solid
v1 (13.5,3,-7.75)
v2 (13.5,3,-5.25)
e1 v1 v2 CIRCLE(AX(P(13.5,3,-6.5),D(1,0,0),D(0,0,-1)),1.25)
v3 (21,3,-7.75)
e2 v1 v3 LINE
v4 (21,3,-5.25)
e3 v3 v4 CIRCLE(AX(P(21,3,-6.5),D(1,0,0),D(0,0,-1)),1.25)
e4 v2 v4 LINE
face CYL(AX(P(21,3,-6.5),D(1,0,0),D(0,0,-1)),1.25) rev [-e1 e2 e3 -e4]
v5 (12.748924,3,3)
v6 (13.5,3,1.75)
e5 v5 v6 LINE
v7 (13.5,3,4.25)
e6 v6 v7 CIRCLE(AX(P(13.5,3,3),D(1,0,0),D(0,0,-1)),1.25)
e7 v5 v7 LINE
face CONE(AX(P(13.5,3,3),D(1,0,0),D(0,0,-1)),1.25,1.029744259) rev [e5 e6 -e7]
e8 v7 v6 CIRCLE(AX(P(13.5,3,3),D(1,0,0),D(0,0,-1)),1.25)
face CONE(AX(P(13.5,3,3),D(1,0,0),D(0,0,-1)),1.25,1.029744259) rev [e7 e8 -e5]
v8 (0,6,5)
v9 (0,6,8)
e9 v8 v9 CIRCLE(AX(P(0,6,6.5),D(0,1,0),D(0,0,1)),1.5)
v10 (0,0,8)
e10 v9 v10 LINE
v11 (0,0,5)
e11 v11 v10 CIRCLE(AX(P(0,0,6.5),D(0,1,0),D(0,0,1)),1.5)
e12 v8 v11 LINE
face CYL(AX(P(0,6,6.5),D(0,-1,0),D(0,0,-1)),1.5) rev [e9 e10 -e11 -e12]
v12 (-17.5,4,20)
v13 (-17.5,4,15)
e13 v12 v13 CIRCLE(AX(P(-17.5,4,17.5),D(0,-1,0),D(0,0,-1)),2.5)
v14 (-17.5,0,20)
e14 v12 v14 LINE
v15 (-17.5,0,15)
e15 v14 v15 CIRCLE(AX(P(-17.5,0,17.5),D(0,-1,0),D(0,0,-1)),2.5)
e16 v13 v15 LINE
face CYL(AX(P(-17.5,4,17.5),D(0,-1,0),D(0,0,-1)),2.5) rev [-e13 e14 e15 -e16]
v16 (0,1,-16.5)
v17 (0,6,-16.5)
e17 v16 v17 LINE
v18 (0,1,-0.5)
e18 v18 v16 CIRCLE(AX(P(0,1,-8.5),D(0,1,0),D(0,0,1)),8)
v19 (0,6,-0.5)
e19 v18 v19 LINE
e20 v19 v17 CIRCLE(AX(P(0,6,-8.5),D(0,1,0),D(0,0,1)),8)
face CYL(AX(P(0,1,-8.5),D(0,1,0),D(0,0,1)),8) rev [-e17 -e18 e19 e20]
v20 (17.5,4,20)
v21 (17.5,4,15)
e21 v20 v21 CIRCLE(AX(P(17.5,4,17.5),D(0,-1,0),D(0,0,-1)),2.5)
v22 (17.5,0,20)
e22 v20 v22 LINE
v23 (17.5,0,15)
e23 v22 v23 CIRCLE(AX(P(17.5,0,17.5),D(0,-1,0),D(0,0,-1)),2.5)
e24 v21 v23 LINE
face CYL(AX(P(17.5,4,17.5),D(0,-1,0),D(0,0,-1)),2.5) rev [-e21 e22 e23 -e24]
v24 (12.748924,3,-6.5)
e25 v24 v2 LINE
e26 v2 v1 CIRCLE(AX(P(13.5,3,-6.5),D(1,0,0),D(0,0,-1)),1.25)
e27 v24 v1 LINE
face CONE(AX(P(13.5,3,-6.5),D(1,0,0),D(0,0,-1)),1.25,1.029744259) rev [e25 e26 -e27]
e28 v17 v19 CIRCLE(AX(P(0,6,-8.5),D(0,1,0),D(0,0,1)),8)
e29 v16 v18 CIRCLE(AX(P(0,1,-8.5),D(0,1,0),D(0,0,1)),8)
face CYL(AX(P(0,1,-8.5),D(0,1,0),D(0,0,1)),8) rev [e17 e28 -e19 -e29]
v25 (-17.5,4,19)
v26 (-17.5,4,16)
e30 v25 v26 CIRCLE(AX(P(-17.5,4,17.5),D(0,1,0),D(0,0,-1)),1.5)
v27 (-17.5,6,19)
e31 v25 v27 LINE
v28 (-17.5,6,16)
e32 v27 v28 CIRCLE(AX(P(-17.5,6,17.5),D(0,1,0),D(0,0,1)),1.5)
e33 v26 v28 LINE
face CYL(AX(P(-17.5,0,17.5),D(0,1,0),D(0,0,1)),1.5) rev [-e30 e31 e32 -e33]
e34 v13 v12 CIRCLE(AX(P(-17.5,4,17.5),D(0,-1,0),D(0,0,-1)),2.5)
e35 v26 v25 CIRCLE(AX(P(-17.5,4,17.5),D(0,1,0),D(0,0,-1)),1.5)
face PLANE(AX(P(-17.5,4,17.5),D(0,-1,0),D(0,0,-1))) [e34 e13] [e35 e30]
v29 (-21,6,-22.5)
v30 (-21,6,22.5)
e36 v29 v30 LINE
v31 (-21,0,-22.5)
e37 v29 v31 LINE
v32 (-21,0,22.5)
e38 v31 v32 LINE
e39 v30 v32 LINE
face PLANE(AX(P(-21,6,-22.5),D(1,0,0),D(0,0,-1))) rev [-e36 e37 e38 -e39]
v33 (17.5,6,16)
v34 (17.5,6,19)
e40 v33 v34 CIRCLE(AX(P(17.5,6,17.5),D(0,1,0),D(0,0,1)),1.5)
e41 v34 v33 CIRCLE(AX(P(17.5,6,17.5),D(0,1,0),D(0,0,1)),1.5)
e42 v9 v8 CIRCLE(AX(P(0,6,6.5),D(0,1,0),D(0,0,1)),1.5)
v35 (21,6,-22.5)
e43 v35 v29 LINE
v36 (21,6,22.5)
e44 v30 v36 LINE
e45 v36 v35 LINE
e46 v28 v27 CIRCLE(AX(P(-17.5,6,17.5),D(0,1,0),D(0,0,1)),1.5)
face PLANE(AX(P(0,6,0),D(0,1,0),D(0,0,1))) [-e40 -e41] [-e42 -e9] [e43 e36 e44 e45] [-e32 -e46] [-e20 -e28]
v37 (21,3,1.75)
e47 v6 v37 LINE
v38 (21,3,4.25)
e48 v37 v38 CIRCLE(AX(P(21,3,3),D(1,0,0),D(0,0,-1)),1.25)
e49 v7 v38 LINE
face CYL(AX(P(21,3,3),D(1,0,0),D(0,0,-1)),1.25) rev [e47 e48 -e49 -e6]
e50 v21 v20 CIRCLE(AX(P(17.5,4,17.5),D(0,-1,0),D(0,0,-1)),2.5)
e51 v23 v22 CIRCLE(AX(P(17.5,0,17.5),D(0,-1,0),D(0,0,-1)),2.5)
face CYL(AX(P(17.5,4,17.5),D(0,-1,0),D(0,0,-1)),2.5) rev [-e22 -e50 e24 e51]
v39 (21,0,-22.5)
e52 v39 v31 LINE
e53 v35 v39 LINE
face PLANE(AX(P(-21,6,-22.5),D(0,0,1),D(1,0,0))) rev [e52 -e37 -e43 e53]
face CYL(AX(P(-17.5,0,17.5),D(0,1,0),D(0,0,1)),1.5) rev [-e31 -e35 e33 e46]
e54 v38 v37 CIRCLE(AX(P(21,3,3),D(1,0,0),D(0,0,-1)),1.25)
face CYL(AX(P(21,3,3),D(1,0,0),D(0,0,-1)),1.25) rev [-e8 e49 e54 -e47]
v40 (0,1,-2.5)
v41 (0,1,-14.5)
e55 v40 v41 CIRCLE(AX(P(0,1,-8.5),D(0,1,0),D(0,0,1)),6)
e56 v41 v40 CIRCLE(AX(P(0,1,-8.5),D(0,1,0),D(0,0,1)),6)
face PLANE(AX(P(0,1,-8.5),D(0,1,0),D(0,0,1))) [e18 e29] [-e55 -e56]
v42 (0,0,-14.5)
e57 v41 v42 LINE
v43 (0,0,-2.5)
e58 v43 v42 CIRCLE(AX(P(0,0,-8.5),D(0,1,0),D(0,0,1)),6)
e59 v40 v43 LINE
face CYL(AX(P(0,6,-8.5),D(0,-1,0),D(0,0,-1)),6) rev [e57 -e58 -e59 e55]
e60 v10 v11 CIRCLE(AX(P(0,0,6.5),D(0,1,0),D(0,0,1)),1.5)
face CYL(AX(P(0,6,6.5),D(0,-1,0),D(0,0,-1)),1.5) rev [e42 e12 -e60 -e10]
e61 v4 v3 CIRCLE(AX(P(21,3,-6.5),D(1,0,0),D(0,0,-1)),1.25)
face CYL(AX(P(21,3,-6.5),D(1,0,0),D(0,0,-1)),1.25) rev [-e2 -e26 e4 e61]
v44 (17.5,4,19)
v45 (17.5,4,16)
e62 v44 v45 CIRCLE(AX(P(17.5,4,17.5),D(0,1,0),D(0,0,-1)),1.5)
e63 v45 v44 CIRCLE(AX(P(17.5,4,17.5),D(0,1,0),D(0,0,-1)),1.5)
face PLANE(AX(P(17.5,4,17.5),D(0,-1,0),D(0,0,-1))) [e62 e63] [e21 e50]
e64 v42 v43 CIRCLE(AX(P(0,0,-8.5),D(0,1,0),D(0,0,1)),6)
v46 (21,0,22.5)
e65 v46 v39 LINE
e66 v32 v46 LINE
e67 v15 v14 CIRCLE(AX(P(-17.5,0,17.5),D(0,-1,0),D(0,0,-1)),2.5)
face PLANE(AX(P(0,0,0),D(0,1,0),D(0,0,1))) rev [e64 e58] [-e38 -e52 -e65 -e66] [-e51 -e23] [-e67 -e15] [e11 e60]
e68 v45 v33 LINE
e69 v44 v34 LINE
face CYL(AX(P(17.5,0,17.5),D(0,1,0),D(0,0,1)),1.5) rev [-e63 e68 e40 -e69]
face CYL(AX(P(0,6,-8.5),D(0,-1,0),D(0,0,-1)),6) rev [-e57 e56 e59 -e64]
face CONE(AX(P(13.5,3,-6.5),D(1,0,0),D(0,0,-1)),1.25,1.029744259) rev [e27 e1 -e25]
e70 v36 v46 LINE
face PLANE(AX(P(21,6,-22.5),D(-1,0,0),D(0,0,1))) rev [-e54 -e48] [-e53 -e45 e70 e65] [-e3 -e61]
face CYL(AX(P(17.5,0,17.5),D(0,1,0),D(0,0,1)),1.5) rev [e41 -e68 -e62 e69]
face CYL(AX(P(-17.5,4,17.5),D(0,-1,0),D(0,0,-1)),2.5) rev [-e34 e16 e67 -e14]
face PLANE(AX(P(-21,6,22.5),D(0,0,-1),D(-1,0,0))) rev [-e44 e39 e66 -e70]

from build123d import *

# Parameters (mm, degrees)
SKETCH1_W             = 42
SKETCH1_H             = 45
SKETCH1_R             = 6
SKETCH1_R_2           = 1.5
BOSS_EXTRUDE1_DEPTH   = 6
SKETCH3_R             = 8
CUT_EXTRUDE1_DEPTH    = 5
SKETCH4_R             = 1.5
CUT_EXTRUDE2_DEPTH    = 32.356817441
SKETCH5_R             = 2.5
CUT_EXTRUDE3_DEPTH    = 4
SKETCH6_R             = 1
CUT_EXTRUDE4_DEPTH    = 2
M3_TAPPED_HOLE1_D     = 2.5
M3_TAPPED_HOLE1_DEPTH = 7.5
M3_TAPPED_HOLE1_TIP   = 0.751075774


with BuildPart() as part:
    # Sketch1 → Boss-Extrude1 (new body)
    with BuildSketch(Plane(origin=(0, 0, 0), x_dir=(1, 0, 0), z_dir=(0, 1, 0))):
        Rectangle(SKETCH1_W, SKETCH1_H)
        with Locations(Location((0, 8.5, 0), (0, 0, 270))):
            Circle(SKETCH1_R, mode=Mode.SUBTRACT)
        with Locations(Location((0, -6.5, 0), (0, 0, 270))):
            Circle(SKETCH1_R_2, mode=Mode.SUBTRACT)
    extrude(amount=BOSS_EXTRUDE1_DEPTH)

    # Sketch3 → Cut-Extrude1 (cut)
    with BuildSketch(Plane(origin=(0, 6, 0), x_dir=(1, 0, 0), z_dir=(0, 1, 0))):
        with Locations(Location((0, 8.5, 0), (0, 0, 270))):
            Circle(SKETCH3_R)
    extrude(amount=-CUT_EXTRUDE1_DEPTH, mode=Mode.SUBTRACT)

    # Sketch4 → Cut-Extrude2 (cut, through all)
    with BuildSketch(Plane(origin=(0, 6, 0), x_dir=(1, 0, 0), z_dir=(0, 1, 0))):
        with Locations(Location((-17.5, -17.5, 0), (0, 0, 270))):
            Circle(SKETCH4_R)
        with Locations(Location((17.5, -17.5, 0), (0, 0, 270))):
            Circle(SKETCH4_R)
    extrude(amount=-CUT_EXTRUDE2_DEPTH, mode=Mode.SUBTRACT)

    # Sketch5 → Cut-Extrude3 (cut)
    with BuildSketch(Plane.XZ):
        with Locations(Location((17.5, 17.5, 0), (0, 0, 270))):
            Circle(SKETCH5_R)
        with Locations(Location((-17.5, 17.5, 0), (0, 0, 270))):
            Circle(SKETCH5_R)
    extrude(amount=-CUT_EXTRUDE3_DEPTH, mode=Mode.SUBTRACT)

    # Sketch6 → Cut-Extrude4 (cut)
    with BuildSketch(Plane(origin=(21, 0, 0), x_dir=(0, 0, -1), z_dir=(1, 0, 0))):
        with Locations((6.5, 3)):
            Circle(SKETCH6_R)
        with Locations((-3, 3)):
            Circle(SKETCH6_R)
    extrude(amount=-CUT_EXTRUDE4_DEPTH, mode=Mode.SUBTRACT)

    # M3 Tapped Hole1
    with Locations(Plane(origin=(21, 0, 0), x_dir=(0, 0, -1), z_dir=(1, 0, 0))):
        with Locations((6.5, 3), (-3, 3)):
            Hole(M3_TAPPED_HOLE1_D / 2, depth=M3_TAPPED_HOLE1_DEPTH)
            with Locations((0, 0, -(M3_TAPPED_HOLE1_DEPTH + M3_TAPPED_HOLE1_TIP / 2))):  # 118° drill point
                Cone(0, M3_TAPPED_HOLE1_D / 2, M3_TAPPED_HOLE1_TIP, mode=Mode.SUBTRACT)


solid = part.part
